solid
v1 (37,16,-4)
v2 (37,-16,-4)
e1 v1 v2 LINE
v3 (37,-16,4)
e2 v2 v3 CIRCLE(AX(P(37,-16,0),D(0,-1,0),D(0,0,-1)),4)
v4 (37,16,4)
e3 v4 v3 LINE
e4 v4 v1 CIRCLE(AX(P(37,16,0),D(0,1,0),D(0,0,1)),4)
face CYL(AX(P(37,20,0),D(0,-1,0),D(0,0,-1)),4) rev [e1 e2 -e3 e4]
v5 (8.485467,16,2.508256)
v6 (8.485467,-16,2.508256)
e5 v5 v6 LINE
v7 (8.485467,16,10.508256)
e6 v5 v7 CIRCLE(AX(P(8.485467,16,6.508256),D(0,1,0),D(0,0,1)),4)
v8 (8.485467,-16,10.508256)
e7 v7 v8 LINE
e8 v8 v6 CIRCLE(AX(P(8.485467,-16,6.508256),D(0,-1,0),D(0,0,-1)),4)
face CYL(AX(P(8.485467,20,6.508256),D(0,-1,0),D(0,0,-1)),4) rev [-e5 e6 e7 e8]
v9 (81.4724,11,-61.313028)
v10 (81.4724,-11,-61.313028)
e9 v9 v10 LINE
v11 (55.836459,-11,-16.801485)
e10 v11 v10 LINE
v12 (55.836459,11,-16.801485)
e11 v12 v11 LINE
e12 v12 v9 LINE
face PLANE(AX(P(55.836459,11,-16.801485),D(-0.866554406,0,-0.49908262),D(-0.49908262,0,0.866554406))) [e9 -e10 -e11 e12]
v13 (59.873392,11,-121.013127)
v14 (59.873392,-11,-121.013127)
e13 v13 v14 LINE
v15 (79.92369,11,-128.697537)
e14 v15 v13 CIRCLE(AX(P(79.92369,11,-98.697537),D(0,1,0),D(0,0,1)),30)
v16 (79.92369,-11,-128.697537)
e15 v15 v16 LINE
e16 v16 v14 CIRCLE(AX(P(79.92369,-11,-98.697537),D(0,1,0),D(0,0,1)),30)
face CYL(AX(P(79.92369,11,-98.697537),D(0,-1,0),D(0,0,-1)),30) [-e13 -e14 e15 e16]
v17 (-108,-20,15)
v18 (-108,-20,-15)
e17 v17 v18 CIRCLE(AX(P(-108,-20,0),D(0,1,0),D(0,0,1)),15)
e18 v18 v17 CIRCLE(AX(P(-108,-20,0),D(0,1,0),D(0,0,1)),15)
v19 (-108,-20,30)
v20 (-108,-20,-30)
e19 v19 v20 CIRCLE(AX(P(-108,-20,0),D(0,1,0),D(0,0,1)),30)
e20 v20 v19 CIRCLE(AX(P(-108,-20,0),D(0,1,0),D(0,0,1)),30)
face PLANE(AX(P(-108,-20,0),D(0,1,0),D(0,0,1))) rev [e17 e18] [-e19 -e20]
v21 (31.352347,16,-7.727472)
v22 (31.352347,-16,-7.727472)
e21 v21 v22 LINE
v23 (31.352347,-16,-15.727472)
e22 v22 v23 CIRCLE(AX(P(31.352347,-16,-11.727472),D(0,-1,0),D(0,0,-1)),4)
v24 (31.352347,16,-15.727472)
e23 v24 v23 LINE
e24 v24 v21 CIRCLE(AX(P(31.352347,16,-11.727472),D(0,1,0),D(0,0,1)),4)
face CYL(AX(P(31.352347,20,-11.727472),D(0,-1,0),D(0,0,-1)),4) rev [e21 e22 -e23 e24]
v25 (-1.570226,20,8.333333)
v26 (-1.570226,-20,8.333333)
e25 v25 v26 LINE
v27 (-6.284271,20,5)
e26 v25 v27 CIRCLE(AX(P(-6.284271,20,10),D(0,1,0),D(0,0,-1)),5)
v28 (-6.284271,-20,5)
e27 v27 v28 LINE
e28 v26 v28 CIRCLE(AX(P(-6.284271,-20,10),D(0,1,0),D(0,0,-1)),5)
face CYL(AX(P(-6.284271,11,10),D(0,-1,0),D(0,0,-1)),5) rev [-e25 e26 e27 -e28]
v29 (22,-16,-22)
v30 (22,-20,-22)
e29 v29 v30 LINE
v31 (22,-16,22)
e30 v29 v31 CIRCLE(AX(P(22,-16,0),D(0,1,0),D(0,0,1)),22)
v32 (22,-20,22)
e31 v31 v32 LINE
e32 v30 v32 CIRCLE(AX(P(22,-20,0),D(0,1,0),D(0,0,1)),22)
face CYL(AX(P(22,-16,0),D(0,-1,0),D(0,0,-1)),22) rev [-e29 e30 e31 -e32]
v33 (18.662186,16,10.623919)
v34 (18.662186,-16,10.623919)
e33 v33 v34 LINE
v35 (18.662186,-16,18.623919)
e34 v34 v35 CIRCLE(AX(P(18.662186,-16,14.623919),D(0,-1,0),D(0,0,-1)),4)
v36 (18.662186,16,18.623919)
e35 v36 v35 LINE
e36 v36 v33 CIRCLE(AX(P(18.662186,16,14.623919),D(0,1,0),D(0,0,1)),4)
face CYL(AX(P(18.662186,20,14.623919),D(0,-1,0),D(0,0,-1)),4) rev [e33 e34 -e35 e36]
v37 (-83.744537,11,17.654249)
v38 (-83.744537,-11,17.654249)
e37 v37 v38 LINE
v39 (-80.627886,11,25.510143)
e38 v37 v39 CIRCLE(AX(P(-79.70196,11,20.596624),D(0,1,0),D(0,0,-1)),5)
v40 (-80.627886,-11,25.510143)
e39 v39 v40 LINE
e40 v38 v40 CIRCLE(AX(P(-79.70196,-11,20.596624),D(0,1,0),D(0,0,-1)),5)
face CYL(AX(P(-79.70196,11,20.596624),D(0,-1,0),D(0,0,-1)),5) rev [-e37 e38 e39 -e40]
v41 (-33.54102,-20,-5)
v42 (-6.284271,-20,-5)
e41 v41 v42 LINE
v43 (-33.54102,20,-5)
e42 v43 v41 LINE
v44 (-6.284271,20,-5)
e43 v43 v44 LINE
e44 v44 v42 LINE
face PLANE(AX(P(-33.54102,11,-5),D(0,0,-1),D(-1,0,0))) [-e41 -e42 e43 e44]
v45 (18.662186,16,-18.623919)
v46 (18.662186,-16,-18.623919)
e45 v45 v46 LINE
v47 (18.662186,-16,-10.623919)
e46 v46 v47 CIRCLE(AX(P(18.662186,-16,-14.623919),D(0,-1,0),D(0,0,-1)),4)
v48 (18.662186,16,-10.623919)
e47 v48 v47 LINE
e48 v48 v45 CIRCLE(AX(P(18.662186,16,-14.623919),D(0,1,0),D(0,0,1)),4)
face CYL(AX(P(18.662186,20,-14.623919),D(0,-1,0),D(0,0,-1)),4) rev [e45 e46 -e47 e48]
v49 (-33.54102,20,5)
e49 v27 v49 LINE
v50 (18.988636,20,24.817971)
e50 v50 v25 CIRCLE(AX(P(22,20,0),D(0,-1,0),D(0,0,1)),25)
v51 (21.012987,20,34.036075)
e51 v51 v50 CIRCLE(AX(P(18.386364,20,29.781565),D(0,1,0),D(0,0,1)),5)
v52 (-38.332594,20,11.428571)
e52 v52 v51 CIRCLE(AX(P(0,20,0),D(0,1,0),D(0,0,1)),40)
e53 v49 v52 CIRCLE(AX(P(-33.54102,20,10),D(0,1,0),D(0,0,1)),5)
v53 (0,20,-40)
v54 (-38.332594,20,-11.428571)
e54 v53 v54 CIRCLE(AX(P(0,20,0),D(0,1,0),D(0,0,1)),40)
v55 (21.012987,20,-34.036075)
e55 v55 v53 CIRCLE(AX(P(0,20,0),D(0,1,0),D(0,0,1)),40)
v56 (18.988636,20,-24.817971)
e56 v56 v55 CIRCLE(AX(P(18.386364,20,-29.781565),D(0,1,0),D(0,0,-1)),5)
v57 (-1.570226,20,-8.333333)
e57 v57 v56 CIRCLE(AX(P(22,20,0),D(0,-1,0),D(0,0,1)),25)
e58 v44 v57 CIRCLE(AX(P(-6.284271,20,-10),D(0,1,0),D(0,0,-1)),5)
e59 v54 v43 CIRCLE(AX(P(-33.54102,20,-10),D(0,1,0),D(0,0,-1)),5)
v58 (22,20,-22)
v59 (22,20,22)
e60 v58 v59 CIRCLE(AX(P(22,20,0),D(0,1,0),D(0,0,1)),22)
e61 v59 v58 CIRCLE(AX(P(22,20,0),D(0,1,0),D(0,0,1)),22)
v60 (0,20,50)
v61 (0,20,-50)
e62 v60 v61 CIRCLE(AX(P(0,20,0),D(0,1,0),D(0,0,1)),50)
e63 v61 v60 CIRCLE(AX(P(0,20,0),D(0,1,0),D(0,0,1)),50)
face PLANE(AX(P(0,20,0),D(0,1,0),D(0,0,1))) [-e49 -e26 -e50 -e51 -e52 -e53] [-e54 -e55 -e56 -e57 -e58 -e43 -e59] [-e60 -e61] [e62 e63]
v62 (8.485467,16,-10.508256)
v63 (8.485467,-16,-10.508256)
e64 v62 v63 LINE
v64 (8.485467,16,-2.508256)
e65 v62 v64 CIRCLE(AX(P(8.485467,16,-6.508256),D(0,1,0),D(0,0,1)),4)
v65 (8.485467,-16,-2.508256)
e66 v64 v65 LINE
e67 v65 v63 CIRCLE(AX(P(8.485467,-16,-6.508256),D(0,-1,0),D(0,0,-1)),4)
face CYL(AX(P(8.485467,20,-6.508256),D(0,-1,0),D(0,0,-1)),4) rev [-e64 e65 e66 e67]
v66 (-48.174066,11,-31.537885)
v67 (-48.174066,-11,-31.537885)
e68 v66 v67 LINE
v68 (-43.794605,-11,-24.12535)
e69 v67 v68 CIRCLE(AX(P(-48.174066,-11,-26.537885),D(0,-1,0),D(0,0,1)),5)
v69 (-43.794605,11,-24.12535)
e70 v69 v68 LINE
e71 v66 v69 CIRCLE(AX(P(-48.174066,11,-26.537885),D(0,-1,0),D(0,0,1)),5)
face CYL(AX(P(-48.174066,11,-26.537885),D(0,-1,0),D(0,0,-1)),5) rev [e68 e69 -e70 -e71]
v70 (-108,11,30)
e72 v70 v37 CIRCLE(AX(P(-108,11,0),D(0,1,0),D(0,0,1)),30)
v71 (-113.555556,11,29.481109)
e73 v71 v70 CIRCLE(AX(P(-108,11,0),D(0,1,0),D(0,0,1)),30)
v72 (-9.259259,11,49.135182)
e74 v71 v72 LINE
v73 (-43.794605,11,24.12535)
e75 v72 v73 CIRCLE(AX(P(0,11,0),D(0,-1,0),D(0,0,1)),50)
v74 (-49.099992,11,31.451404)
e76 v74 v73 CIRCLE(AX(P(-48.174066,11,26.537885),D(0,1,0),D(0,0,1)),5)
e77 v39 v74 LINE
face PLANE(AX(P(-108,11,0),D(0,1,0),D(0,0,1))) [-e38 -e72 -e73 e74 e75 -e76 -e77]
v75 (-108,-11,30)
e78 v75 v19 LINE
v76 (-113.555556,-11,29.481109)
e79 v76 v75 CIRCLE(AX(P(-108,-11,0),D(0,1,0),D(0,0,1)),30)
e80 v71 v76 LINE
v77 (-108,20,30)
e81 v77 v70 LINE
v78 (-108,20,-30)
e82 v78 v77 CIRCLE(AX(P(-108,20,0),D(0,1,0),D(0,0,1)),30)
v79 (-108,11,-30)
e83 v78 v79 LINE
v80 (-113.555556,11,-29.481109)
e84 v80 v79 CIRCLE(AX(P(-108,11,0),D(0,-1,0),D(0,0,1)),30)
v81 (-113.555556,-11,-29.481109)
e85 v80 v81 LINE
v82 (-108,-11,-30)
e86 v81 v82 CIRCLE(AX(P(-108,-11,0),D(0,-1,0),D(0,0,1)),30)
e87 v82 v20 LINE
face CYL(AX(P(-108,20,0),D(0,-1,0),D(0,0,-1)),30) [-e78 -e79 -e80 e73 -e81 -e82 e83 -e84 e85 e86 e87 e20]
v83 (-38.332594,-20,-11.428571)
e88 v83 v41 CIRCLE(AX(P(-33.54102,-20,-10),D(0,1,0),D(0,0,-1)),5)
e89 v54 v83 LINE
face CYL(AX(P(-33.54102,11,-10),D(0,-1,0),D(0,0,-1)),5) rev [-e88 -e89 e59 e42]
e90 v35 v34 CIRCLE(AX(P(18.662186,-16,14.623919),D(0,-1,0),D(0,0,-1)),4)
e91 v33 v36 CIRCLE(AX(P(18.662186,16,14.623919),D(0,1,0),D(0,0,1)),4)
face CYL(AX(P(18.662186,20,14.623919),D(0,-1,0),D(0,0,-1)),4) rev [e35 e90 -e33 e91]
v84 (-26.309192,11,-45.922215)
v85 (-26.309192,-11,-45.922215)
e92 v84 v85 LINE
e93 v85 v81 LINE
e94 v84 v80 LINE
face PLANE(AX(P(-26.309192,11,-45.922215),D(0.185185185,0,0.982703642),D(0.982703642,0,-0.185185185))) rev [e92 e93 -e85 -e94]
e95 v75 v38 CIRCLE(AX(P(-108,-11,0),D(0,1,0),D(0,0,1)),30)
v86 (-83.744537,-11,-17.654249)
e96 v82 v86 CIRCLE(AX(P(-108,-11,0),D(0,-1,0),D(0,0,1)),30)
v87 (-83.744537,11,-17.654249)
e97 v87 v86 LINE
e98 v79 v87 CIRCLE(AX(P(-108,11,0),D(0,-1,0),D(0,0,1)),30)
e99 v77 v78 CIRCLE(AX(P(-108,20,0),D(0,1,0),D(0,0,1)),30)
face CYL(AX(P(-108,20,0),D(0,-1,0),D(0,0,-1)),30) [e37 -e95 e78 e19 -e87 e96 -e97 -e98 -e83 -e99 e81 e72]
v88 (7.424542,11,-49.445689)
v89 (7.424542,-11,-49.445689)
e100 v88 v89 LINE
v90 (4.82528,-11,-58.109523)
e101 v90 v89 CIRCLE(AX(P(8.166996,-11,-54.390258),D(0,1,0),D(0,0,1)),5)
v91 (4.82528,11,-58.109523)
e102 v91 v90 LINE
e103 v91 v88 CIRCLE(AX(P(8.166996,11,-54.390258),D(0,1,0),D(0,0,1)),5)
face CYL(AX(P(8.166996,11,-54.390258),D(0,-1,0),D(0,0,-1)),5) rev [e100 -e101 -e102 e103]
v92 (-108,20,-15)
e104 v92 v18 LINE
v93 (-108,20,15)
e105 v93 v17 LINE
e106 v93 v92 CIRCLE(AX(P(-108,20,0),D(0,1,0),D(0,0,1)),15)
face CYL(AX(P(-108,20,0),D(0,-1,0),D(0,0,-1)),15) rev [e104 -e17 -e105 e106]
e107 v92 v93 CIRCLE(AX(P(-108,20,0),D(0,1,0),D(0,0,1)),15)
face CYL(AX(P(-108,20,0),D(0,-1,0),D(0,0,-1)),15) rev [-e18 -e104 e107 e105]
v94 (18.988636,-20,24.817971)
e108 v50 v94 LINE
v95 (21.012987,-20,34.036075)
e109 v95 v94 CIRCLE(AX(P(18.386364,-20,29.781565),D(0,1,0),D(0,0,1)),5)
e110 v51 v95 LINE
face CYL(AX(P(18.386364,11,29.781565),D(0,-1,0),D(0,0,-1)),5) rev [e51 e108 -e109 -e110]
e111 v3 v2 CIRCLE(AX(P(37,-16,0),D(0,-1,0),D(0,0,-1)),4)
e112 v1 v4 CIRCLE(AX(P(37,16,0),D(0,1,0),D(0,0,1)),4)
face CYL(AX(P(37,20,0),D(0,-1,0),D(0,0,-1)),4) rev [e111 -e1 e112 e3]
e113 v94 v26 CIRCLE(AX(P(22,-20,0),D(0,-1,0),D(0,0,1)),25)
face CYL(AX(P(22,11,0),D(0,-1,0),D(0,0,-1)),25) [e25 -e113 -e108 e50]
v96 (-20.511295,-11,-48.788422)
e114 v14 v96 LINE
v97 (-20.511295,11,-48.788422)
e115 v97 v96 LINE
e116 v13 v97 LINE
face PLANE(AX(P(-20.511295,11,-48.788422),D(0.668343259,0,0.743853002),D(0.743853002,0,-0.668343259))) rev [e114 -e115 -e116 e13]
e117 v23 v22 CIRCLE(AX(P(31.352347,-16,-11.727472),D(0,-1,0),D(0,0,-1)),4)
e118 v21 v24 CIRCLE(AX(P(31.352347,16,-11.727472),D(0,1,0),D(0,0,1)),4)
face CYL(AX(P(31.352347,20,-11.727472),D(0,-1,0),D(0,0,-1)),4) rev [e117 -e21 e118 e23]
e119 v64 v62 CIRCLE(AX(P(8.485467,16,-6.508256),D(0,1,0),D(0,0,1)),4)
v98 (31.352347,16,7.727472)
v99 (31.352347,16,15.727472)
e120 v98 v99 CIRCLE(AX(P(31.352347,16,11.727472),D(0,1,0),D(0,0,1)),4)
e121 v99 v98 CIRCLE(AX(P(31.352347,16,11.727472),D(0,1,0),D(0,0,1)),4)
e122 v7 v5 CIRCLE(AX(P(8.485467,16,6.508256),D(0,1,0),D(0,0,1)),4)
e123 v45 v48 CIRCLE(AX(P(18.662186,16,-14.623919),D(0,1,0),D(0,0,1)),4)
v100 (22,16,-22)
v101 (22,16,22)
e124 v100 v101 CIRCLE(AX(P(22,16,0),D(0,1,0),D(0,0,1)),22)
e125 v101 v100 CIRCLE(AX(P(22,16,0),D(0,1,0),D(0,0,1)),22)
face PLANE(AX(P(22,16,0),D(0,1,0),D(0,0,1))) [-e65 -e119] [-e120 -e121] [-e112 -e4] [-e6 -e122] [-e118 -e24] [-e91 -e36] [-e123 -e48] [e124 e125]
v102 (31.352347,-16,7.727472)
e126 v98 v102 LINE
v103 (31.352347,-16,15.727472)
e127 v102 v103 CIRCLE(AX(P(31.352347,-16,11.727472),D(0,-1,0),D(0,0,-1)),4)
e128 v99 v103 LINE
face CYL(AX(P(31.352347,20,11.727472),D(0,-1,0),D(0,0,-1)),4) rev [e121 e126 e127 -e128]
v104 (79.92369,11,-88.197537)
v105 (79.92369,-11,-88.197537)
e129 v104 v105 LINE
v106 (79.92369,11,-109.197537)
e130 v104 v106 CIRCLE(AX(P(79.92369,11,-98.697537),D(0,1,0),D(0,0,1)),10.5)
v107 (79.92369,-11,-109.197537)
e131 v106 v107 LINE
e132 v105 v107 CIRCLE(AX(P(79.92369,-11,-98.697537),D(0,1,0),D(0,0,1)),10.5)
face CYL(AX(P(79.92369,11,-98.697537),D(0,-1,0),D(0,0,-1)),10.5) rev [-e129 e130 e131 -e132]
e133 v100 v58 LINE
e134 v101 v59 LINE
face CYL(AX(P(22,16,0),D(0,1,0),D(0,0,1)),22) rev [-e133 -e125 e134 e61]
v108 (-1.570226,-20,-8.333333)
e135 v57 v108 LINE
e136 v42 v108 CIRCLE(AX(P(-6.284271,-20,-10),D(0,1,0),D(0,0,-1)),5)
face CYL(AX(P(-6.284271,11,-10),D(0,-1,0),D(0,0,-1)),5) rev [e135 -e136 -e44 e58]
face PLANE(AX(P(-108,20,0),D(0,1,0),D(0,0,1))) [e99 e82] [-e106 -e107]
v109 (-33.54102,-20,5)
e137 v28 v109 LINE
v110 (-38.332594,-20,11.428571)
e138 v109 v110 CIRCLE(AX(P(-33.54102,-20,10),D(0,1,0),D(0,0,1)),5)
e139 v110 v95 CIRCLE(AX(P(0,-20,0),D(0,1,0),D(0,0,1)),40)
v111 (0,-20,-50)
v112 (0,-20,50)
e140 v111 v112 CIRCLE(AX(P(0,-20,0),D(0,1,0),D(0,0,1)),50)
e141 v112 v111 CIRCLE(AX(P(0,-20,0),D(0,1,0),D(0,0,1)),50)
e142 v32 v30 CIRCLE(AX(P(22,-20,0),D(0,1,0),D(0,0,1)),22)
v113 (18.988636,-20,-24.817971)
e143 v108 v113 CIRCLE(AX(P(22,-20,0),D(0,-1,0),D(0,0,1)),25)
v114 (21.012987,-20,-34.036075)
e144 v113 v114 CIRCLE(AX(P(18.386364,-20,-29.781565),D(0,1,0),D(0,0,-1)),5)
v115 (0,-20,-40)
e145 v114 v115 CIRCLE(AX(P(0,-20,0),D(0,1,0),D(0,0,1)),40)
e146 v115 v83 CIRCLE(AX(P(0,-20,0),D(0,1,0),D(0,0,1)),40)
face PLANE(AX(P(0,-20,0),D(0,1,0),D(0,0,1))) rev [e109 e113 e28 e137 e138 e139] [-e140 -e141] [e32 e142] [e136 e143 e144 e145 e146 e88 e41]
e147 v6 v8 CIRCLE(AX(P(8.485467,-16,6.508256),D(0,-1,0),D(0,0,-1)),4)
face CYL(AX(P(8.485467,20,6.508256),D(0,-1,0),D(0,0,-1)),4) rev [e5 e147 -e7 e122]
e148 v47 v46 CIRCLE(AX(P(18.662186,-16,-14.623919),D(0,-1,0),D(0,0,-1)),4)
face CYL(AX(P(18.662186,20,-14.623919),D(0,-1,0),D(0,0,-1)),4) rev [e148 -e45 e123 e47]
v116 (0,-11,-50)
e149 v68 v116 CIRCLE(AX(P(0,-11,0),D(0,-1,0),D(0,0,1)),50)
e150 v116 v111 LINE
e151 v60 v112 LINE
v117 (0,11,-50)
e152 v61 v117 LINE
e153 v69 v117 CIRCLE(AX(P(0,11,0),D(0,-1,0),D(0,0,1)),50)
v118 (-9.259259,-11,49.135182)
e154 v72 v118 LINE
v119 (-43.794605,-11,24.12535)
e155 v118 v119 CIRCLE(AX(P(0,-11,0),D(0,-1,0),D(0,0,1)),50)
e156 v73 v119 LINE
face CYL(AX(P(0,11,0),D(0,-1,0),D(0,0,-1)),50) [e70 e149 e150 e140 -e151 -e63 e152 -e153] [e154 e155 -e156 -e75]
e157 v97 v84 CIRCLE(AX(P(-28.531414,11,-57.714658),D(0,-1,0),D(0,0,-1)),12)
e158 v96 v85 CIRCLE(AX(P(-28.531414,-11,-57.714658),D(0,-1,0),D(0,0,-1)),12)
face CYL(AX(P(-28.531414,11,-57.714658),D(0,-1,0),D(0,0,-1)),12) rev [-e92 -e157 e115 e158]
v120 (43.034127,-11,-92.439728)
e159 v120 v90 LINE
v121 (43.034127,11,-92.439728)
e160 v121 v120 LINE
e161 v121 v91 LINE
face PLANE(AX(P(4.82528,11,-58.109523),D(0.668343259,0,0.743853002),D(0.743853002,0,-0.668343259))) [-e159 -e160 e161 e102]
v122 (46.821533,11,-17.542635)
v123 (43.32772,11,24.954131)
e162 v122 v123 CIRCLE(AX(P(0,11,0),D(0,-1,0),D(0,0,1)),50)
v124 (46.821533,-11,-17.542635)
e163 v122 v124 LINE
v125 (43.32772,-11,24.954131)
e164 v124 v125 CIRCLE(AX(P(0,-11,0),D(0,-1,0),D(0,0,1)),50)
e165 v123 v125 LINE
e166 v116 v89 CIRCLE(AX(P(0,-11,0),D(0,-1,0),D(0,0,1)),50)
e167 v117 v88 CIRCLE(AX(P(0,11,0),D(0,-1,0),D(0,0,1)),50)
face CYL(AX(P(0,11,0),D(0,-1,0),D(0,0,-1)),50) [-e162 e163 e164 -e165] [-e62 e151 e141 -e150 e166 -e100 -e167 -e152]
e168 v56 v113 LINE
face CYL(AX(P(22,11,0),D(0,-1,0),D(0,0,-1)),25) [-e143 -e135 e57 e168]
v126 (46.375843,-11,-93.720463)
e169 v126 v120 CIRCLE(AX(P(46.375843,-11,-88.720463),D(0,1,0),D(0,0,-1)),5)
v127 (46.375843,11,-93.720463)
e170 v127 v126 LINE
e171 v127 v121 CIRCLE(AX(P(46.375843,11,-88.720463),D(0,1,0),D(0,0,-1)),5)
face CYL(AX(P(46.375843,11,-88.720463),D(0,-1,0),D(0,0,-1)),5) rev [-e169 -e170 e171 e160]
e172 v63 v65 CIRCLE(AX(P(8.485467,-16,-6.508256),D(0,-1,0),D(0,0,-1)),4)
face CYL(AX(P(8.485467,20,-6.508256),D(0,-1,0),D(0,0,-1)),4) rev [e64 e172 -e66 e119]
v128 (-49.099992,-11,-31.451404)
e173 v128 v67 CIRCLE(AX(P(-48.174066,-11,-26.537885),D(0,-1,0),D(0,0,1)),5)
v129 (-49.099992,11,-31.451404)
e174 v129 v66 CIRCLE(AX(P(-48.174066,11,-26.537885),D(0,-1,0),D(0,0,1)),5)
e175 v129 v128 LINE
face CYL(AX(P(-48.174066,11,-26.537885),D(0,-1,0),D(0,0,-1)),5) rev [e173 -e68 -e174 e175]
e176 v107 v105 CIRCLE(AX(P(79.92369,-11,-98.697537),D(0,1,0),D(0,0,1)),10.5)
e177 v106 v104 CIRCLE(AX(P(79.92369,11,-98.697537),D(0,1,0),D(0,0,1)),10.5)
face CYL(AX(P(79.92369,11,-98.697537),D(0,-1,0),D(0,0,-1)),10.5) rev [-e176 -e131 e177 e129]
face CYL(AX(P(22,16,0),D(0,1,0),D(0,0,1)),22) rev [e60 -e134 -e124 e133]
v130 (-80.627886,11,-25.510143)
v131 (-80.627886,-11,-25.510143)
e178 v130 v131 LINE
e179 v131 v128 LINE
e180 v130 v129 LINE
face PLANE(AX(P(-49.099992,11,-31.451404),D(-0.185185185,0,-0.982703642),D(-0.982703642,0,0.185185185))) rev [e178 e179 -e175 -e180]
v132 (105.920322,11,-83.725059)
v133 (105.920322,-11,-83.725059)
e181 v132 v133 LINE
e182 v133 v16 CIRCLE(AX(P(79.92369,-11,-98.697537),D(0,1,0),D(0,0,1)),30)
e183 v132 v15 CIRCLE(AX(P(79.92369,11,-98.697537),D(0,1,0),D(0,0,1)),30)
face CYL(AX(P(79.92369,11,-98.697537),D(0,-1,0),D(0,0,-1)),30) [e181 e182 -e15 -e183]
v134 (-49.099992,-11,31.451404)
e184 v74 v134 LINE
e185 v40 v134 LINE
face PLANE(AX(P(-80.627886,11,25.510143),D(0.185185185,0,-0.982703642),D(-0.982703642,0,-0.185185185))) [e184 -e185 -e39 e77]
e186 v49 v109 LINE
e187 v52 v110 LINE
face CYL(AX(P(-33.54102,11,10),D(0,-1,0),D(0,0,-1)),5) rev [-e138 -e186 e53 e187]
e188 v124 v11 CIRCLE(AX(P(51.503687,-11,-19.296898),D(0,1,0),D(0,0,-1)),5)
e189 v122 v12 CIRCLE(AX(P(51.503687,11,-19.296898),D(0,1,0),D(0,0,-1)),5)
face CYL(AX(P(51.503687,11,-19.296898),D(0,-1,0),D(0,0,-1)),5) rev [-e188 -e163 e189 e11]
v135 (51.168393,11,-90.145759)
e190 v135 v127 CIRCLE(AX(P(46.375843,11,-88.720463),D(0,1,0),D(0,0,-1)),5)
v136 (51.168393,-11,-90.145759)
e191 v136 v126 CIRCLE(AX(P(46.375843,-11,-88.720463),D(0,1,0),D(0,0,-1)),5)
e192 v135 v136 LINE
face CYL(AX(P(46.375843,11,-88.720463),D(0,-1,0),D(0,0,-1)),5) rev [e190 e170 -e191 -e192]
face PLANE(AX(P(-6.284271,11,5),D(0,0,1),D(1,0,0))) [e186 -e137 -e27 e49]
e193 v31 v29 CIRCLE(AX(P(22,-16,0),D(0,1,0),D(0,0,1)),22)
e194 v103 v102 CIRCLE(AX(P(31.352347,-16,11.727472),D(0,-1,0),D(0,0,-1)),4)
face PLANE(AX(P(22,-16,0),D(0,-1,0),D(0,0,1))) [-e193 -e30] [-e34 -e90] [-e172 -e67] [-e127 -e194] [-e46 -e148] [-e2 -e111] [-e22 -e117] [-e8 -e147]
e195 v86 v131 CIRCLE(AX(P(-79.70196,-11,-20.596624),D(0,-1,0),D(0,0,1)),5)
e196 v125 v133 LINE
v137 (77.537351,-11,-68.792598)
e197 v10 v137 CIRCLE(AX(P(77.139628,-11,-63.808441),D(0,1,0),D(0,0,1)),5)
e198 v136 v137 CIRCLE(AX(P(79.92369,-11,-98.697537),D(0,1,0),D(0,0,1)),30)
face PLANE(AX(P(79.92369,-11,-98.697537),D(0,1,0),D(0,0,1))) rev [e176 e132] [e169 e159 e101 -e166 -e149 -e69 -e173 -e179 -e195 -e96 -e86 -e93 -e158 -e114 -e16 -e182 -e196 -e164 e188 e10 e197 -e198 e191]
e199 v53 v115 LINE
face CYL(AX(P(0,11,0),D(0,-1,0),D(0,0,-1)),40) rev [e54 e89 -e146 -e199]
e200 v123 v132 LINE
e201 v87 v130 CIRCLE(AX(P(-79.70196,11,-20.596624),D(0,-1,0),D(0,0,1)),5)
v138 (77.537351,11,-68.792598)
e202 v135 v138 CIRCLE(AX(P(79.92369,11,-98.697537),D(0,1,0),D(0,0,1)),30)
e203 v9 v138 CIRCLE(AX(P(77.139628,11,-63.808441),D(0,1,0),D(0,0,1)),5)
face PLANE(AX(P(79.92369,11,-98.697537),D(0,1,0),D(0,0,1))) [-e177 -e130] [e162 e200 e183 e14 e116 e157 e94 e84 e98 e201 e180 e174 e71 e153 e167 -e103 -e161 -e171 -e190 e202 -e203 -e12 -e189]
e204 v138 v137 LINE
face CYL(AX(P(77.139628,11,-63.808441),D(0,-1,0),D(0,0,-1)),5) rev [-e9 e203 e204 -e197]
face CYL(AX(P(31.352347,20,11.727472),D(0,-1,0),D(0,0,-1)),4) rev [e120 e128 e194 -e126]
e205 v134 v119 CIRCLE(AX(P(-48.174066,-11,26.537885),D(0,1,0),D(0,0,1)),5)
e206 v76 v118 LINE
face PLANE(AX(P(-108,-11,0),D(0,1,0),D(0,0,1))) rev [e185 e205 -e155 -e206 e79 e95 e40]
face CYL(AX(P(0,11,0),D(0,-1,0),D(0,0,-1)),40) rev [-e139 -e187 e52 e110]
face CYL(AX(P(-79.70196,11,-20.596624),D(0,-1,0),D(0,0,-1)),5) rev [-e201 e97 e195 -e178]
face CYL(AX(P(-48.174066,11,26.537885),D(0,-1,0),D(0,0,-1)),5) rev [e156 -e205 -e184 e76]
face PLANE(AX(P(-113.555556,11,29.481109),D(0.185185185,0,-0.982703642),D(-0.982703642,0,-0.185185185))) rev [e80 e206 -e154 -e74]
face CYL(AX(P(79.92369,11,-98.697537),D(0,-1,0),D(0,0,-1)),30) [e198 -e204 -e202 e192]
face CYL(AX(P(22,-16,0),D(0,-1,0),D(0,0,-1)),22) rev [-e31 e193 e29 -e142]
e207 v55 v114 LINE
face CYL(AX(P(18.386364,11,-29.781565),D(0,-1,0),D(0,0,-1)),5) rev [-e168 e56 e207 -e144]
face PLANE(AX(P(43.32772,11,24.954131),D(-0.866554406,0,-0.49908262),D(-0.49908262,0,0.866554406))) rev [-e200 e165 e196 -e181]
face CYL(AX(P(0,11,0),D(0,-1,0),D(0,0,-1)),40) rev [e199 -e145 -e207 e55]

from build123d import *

# Parameters (mm, degrees)
HUB_AND_ARM_PROFILE_SKETCH_R   = 50
HUB_AND_ARM_PROFILE_SKETCH_R_2 = 4
HUB_AND_ARM_BODY_DEPTH         = 20
HUB_AND_ARM_PROFILE_SKETCH_R_3 = 30
HUB_AND_ARM_PROFILE_SKETCH_R_4 = 15
HUB_AND_ARM_BODY_2_DEPTH       = 20
HUB_RECESS_SKETCH_R            = 22
HUB_RECESS_DEPTH               = 4
ANGLED_ARM_SKETCH_R            = 30
ANGLED_ARM_SKETCH_R_2          = 10.5
ANGLED_ARM_BOSS_DEPTH          = 11
ARM_WALL_SKETCH_1_R            = 15
ARM_WALL_SKETCH_1_R_2          = 22
ARM_WALL_BOSS_1_DEPTH          = 11
ARM_WALL_SKETCH_2_R            = 10.5
ARM_WALL_SKETCH_2_R_2          = 22
ARM_WALL_BOSS_2_DEPTH          = 11


with BuildPart() as part:
    # Hub and Arm Profile Sketch → Hub and Arm Body (new, symmetric)
    with BuildSketch(Plane(origin=(0, 0, 0), x_dir=(1, 0, 0), z_dir=(0, 1, 0))):
        with Locations(Location((0, 0, 0), (0, 0, 270))):
            Circle(HUB_AND_ARM_PROFILE_SKETCH_R)
        with Locations(Location((37, 0, 0), (0, 0, 270))):
            Circle(HUB_AND_ARM_PROFILE_SKETCH_R_2, mode=Mode.SUBTRACT)
        with Locations(Location((31.352347028, -11.727472237, 0), (0, 0, 270))):
            Circle(HUB_AND_ARM_PROFILE_SKETCH_R_2, mode=Mode.SUBTRACT)
        with Locations(Location((18.662185991, -14.623918683, 0), (0, 0, 270))):
            Circle(HUB_AND_ARM_PROFILE_SKETCH_R_2, mode=Mode.SUBTRACT)
        with Locations(Location((8.485466981, -6.508256087, 0), (0, 0, 270))):
            Circle(HUB_AND_ARM_PROFILE_SKETCH_R_2, mode=Mode.SUBTRACT)
        with Locations(Location((8.485466981, 6.508256087, 0), (0, 0, 270))):
            Circle(HUB_AND_ARM_PROFILE_SKETCH_R_2, mode=Mode.SUBTRACT)
        with Locations(Location((18.662185991, 14.623918683, 0), (0, 0, 270))):
            Circle(HUB_AND_ARM_PROFILE_SKETCH_R_2, mode=Mode.SUBTRACT)
        with Locations(Location((31.352347028, 11.727472237, 0), (0, 0, 270))):
            Circle(HUB_AND_ARM_PROFILE_SKETCH_R_2, mode=Mode.SUBTRACT)
        with BuildLine():
            Line((-33.541019662, 5), (-6.284271247, 5))
            ThreePointArc((-6.284271247, 5), (-3.397519902, 5.917517095), (-1.57022604, 8.333333333))
            ThreePointArc((-1.57022604, 8.333333333), (6.360912817, 19.504331623), (18.988636364, 24.817971091))
            ThreePointArc((18.988636364, 24.817971091), (23.269989417, 28.70909189), (21.012987013, 34.036074638))
            ThreePointArc((21.012987013, 34.036074638), (-14.239627665, 37.37958004), (-38.3325939, 11.428571429))
            ThreePointArc((-38.3325939, 11.428571429), (-37.549938291, 7.011928477), (-33.541019662, 5))
        make_face(mode=Mode.SUBTRACT)
        with BuildLine():
            Line((-33.541019662, -5), (-6.284271247, -5))
            ThreePointArc((-6.284271247, -5), (-3.397519902, -5.917517095), (-1.57022604, -8.333333333))
            ThreePointArc((-1.57022604, -8.333333333), (6.360912817, -19.504331623), (18.988636364, -24.817971091))
            ThreePointArc((18.988636364, -24.817971091), (23.269989417, -28.70909189), (21.012987013, -34.036074638))
            ThreePointArc((21.012987013, -34.036074638), (-14.239627665, -37.37958004), (-38.3325939, -11.428571429))
            ThreePointArc((-38.3325939, -11.428571429), (-37.549938291, -7.011928477), (-33.541019662, -5))
        make_face(mode=Mode.SUBTRACT)
    extrude(amount=HUB_AND_ARM_BODY_DEPTH, both=True)

    # Hub Recess Sketch → Hub Recess (cut)
    with BuildSketch(Plane(origin=(0, 20, 0), x_dir=(1, 0, 0), z_dir=(0, 1, 0))):
        with Locations(Location((22, 0, 0), (0, 0, 270))):
            Circle(HUB_RECESS_SKETCH_R)
    hub_recess = extrude(amount=-HUB_RECESS_DEPTH, mode=Mode.SUBTRACT)

    # Hub Recess Mirror: Hub Recess across plane
    add(hub_recess.mirror(Plane.ZX), mode=Mode.SUBTRACT)



with BuildPart() as body_2:
    # Hub and Arm Profile Sketch → Hub and Arm Body 2 (new, symmetric)
    with BuildSketch(Plane(origin=(0, 0, 0), x_dir=(1, 0, 0), z_dir=(0, 1, 0))):
        with Locations(Location((-108, 0, 0), (0, 0, 270))):
            Circle(HUB_AND_ARM_PROFILE_SKETCH_R_3)
        with Locations(Location((-108, 0, 0), (0, 0, 270))):
            Circle(HUB_AND_ARM_PROFILE_SKETCH_R_4, mode=Mode.SUBTRACT)
    extrude(amount=HUB_AND_ARM_BODY_2_DEPTH, both=True)


with BuildPart() as body_3:
    # Angled Arm Sketch → Angled Arm Boss (new, symmetric)
    with BuildSketch(Plane(origin=(0, 0, 0), x_dir=(1, 0, 0), z_dir=(0, 1, 0))):
        with Locations(Location((79.923689663, 98.697537105, 0), (0, 0, 270))):
            Circle(ANGLED_ARM_SKETCH_R)
        with Locations(Location((79.923689663, 98.697537105, 0), (0, 0, 270))):
            Circle(ANGLED_ARM_SKETCH_R_2, mode=Mode.SUBTRACT)
    extrude(amount=ANGLED_ARM_BOSS_DEPTH, both=True)


with BuildPart() as part_1:
    add(part.part)

    add(body_2.part)  # Arm Wall Boss 1 merges body 2
    # Arm Wall Sketch 1 → Arm Wall Boss 1 (add, symmetric)
    with BuildSketch(Plane(origin=(0, 0, 0), x_dir=(1, 0, 0), z_dir=(0, 1, 0))):
        with BuildLine():
            Line((-113.555555556, -29.481109248), (-9.259259259, -49.135182079))
            ThreePointArc((-9.259259259, -49.135182079), (50, 0), (-9.259259259, 49.135182079))
            Line((-9.259259259, 49.135182079), (-113.555555556, 29.481109248))
            ThreePointArc((-113.555555556, 29.481109248), (-138, 0), (-113.555555556, -29.481109248))
        make_face()
        with Locations(Location((-108, 0, 0), (0, 0, 270))):
            Circle(ARM_WALL_SKETCH_1_R, mode=Mode.SUBTRACT)
        with Locations(Location((22, 0, 0), (0, 0, 270))):
            Circle(ARM_WALL_SKETCH_1_R_2, mode=Mode.SUBTRACT)
        with BuildLine():
            Line((-80.62788598, -25.510142573), (-49.099991939, -31.45140365))
            ThreePointArc((-49.099991939, -31.45140365), (-44.12443771, -29.470548159), (-43.794605467, -24.125350402))
            ThreePointArc((-43.794605467, -24.125350402), (-50, 0), (-43.794605467, 24.125350402))
            ThreePointArc((-43.794605467, 24.125350402), (-44.12443771, 29.470548159), (-49.099991939, 31.45140365))
            Line((-49.099991939, 31.45140365), (-80.62788598, 25.510142573))
            ThreePointArc((-80.62788598, 25.510142573), (-84.349569099, 22.440460086), (-83.744537189, 17.654249456))
            ThreePointArc((-83.744537189, 17.654249456), (-78, 0), (-83.744537189, -17.654249456))
            ThreePointArc((-83.744537189, -17.654249456), (-84.349569099, -22.440460086), (-80.62788598, -25.510142573))
        make_face(mode=Mode.SUBTRACT)
        with BuildLine():
            Line((-6.284271247, -5), (-33.541019662, -5))
            ThreePointArc((-33.541019662, -5), (-37.549938291, -7.011928477), (-38.3325939, -11.428571429))
            ThreePointArc((-38.3325939, -11.428571429), (-14.239627665, -37.37958004), (21.012987013, -34.036074638))
            ThreePointArc((21.012987013, -34.036074638), (23.269989417, -28.70909189), (18.988636364, -24.817971091))
            ThreePointArc((18.988636364, -24.817971091), (6.360912817, -19.504331623), (-1.57022604, -8.333333333))
            ThreePointArc((-1.57022604, -8.333333333), (-3.397519902, -5.917517095), (-6.284271247, -5))
        make_face(mode=Mode.SUBTRACT)
        with BuildLine():
            Line((-33.541019662, 5), (-6.284271247, 5))
            ThreePointArc((-6.284271247, 5), (-3.397519902, 5.917517095), (-1.57022604, 8.333333333))
            ThreePointArc((-1.57022604, 8.333333333), (6.360912817, 19.504331623), (18.988636364, 24.817971091))
            ThreePointArc((18.988636364, 24.817971091), (23.269989417, 28.70909189), (21.012987013, 34.036074638))
            ThreePointArc((21.012987013, 34.036074638), (-14.239627665, 37.37958004), (-38.3325939, 11.428571429))
            ThreePointArc((-38.3325939, 11.428571429), (-37.549938291, 7.011928477), (-33.541019662, 5))
        make_face(mode=Mode.SUBTRACT)
    extrude(amount=ARM_WALL_BOSS_1_DEPTH, both=True)


    add(body_3.part)  # Arm Wall Boss 2 merges body 3
    # Arm Wall Sketch 2 → Arm Wall Boss 2 (add, symmetric)
    with BuildSketch(Plane(origin=(0, 0, 0), x_dir=(1, 0, 0), z_dir=(0, 1, 0))):
        with BuildLine():
            Line((-49.099991939, 31.45140365), (-80.62788598, 25.510142573))
            ThreePointArc((-80.62788598, 25.510142573), (-84.349569099, 22.440460086), (-83.744537189, 17.654249456))
            ThreePointArc((-83.744537189, 17.654249456), (-96.936985674, 27.885654269), (-113.555555556, 29.481109248))
            Line((-113.555555556, 29.481109248), (-26.309191814, 45.922214523))
            ThreePointArc((-26.309191814, 45.922214523), (-23.213503206, 46.957343297), (-20.511294927, 48.788422203))
            Line((-20.511294927, 48.788422203), (59.873391891, 121.013127154))
            ThreePointArc((59.873391891, 121.013127154), (98.803301395, 122.011915949), (105.92032184, 83.725058503))
            Line((105.92032184, 83.725058503), (43.327720294, -24.954131003))
            ThreePointArc((43.327720294, -24.954131003), (-24.540851028, -43.56313385), (-43.794605467, 24.125350402))
            ThreePointArc((-43.794605467, 24.125350402), (-44.12443771, 29.470548159), (-49.099991939, 31.45140365))
        make_face()
        with Locations(Location((79.923689663, 98.697537105, 0), (0, 0, 270))):
            Circle(ARM_WALL_SKETCH_2_R, mode=Mode.SUBTRACT)
        with Locations(Location((22, 0, 0), (0, 0, 270))):
            Circle(ARM_WALL_SKETCH_2_R_2, mode=Mode.SUBTRACT)
        with BuildLine():
            Line((55.836458536, 16.801484997), (81.472399581, 61.313028313))
            ThreePointArc((81.472399581, 61.313028313), (81.564600618, 66.136447721), (77.53735071, 68.792597941))
            ThreePointArc((77.53735071, 68.792597941), (61.044077932, 75.383158261), (51.168392937, 90.145758918))
            ThreePointArc((51.168392937, 90.145758918), (47.732973634, 93.532759069), (43.034127187, 92.439727562))
            Line((43.034127187, 92.439727562), (4.825279735, 58.109523105))
            ThreePointArc((4.825279735, 58.109523105), (3.377881635, 52.953461905), (7.424541846, 49.445689179))
            ThreePointArc((7.424541846, 49.445689179), (31.466019552, 38.857298073), (46.821533188, 17.542634634))
            ThreePointArc((46.821533188, 17.542634634), (51.09400063, 14.313710616), (55.836458536, 16.801484997))
        make_face(mode=Mode.SUBTRACT)
        with BuildLine():
            Line((-33.541019662, 5), (-6.284271247, 5))
            ThreePointArc((-6.284271247, 5), (-3.397519902, 5.917517095), (-1.57022604, 8.333333333))
            ThreePointArc((-1.57022604, 8.333333333), (6.360912817, 19.504331623), (18.988636364, 24.817971091))
            ThreePointArc((18.988636364, 24.817971091), (23.269989417, 28.70909189), (21.012987013, 34.036074638))
            ThreePointArc((21.012987013, 34.036074638), (-14.239627665, 37.37958004), (-38.3325939, 11.428571429))
            ThreePointArc((-38.3325939, 11.428571429), (-37.549938291, 7.011928477), (-33.541019662, 5))
        make_face(mode=Mode.SUBTRACT)
        with BuildLine():
            Line((-6.284271247, -5), (-33.541019662, -5))
            ThreePointArc((-33.541019662, -5), (-37.549938291, -7.011928477), (-38.3325939, -11.428571429))
            ThreePointArc((-38.3325939, -11.428571429), (-14.239627665, -37.37958004), (21.012987013, -34.036074638))
            ThreePointArc((21.012987013, -34.036074638), (23.269989417, -28.70909189), (18.988636364, -24.817971091))
            ThreePointArc((18.988636364, -24.817971091), (6.360912817, -19.504331623), (-1.57022604, -8.333333333))
            ThreePointArc((-1.57022604, -8.333333333), (-3.397519902, -5.917517095), (-6.284271247, -5))
        make_face(mode=Mode.SUBTRACT)
    extrude(amount=ARM_WALL_BOSS_2_DEPTH, both=True)


solid = part_1.part
